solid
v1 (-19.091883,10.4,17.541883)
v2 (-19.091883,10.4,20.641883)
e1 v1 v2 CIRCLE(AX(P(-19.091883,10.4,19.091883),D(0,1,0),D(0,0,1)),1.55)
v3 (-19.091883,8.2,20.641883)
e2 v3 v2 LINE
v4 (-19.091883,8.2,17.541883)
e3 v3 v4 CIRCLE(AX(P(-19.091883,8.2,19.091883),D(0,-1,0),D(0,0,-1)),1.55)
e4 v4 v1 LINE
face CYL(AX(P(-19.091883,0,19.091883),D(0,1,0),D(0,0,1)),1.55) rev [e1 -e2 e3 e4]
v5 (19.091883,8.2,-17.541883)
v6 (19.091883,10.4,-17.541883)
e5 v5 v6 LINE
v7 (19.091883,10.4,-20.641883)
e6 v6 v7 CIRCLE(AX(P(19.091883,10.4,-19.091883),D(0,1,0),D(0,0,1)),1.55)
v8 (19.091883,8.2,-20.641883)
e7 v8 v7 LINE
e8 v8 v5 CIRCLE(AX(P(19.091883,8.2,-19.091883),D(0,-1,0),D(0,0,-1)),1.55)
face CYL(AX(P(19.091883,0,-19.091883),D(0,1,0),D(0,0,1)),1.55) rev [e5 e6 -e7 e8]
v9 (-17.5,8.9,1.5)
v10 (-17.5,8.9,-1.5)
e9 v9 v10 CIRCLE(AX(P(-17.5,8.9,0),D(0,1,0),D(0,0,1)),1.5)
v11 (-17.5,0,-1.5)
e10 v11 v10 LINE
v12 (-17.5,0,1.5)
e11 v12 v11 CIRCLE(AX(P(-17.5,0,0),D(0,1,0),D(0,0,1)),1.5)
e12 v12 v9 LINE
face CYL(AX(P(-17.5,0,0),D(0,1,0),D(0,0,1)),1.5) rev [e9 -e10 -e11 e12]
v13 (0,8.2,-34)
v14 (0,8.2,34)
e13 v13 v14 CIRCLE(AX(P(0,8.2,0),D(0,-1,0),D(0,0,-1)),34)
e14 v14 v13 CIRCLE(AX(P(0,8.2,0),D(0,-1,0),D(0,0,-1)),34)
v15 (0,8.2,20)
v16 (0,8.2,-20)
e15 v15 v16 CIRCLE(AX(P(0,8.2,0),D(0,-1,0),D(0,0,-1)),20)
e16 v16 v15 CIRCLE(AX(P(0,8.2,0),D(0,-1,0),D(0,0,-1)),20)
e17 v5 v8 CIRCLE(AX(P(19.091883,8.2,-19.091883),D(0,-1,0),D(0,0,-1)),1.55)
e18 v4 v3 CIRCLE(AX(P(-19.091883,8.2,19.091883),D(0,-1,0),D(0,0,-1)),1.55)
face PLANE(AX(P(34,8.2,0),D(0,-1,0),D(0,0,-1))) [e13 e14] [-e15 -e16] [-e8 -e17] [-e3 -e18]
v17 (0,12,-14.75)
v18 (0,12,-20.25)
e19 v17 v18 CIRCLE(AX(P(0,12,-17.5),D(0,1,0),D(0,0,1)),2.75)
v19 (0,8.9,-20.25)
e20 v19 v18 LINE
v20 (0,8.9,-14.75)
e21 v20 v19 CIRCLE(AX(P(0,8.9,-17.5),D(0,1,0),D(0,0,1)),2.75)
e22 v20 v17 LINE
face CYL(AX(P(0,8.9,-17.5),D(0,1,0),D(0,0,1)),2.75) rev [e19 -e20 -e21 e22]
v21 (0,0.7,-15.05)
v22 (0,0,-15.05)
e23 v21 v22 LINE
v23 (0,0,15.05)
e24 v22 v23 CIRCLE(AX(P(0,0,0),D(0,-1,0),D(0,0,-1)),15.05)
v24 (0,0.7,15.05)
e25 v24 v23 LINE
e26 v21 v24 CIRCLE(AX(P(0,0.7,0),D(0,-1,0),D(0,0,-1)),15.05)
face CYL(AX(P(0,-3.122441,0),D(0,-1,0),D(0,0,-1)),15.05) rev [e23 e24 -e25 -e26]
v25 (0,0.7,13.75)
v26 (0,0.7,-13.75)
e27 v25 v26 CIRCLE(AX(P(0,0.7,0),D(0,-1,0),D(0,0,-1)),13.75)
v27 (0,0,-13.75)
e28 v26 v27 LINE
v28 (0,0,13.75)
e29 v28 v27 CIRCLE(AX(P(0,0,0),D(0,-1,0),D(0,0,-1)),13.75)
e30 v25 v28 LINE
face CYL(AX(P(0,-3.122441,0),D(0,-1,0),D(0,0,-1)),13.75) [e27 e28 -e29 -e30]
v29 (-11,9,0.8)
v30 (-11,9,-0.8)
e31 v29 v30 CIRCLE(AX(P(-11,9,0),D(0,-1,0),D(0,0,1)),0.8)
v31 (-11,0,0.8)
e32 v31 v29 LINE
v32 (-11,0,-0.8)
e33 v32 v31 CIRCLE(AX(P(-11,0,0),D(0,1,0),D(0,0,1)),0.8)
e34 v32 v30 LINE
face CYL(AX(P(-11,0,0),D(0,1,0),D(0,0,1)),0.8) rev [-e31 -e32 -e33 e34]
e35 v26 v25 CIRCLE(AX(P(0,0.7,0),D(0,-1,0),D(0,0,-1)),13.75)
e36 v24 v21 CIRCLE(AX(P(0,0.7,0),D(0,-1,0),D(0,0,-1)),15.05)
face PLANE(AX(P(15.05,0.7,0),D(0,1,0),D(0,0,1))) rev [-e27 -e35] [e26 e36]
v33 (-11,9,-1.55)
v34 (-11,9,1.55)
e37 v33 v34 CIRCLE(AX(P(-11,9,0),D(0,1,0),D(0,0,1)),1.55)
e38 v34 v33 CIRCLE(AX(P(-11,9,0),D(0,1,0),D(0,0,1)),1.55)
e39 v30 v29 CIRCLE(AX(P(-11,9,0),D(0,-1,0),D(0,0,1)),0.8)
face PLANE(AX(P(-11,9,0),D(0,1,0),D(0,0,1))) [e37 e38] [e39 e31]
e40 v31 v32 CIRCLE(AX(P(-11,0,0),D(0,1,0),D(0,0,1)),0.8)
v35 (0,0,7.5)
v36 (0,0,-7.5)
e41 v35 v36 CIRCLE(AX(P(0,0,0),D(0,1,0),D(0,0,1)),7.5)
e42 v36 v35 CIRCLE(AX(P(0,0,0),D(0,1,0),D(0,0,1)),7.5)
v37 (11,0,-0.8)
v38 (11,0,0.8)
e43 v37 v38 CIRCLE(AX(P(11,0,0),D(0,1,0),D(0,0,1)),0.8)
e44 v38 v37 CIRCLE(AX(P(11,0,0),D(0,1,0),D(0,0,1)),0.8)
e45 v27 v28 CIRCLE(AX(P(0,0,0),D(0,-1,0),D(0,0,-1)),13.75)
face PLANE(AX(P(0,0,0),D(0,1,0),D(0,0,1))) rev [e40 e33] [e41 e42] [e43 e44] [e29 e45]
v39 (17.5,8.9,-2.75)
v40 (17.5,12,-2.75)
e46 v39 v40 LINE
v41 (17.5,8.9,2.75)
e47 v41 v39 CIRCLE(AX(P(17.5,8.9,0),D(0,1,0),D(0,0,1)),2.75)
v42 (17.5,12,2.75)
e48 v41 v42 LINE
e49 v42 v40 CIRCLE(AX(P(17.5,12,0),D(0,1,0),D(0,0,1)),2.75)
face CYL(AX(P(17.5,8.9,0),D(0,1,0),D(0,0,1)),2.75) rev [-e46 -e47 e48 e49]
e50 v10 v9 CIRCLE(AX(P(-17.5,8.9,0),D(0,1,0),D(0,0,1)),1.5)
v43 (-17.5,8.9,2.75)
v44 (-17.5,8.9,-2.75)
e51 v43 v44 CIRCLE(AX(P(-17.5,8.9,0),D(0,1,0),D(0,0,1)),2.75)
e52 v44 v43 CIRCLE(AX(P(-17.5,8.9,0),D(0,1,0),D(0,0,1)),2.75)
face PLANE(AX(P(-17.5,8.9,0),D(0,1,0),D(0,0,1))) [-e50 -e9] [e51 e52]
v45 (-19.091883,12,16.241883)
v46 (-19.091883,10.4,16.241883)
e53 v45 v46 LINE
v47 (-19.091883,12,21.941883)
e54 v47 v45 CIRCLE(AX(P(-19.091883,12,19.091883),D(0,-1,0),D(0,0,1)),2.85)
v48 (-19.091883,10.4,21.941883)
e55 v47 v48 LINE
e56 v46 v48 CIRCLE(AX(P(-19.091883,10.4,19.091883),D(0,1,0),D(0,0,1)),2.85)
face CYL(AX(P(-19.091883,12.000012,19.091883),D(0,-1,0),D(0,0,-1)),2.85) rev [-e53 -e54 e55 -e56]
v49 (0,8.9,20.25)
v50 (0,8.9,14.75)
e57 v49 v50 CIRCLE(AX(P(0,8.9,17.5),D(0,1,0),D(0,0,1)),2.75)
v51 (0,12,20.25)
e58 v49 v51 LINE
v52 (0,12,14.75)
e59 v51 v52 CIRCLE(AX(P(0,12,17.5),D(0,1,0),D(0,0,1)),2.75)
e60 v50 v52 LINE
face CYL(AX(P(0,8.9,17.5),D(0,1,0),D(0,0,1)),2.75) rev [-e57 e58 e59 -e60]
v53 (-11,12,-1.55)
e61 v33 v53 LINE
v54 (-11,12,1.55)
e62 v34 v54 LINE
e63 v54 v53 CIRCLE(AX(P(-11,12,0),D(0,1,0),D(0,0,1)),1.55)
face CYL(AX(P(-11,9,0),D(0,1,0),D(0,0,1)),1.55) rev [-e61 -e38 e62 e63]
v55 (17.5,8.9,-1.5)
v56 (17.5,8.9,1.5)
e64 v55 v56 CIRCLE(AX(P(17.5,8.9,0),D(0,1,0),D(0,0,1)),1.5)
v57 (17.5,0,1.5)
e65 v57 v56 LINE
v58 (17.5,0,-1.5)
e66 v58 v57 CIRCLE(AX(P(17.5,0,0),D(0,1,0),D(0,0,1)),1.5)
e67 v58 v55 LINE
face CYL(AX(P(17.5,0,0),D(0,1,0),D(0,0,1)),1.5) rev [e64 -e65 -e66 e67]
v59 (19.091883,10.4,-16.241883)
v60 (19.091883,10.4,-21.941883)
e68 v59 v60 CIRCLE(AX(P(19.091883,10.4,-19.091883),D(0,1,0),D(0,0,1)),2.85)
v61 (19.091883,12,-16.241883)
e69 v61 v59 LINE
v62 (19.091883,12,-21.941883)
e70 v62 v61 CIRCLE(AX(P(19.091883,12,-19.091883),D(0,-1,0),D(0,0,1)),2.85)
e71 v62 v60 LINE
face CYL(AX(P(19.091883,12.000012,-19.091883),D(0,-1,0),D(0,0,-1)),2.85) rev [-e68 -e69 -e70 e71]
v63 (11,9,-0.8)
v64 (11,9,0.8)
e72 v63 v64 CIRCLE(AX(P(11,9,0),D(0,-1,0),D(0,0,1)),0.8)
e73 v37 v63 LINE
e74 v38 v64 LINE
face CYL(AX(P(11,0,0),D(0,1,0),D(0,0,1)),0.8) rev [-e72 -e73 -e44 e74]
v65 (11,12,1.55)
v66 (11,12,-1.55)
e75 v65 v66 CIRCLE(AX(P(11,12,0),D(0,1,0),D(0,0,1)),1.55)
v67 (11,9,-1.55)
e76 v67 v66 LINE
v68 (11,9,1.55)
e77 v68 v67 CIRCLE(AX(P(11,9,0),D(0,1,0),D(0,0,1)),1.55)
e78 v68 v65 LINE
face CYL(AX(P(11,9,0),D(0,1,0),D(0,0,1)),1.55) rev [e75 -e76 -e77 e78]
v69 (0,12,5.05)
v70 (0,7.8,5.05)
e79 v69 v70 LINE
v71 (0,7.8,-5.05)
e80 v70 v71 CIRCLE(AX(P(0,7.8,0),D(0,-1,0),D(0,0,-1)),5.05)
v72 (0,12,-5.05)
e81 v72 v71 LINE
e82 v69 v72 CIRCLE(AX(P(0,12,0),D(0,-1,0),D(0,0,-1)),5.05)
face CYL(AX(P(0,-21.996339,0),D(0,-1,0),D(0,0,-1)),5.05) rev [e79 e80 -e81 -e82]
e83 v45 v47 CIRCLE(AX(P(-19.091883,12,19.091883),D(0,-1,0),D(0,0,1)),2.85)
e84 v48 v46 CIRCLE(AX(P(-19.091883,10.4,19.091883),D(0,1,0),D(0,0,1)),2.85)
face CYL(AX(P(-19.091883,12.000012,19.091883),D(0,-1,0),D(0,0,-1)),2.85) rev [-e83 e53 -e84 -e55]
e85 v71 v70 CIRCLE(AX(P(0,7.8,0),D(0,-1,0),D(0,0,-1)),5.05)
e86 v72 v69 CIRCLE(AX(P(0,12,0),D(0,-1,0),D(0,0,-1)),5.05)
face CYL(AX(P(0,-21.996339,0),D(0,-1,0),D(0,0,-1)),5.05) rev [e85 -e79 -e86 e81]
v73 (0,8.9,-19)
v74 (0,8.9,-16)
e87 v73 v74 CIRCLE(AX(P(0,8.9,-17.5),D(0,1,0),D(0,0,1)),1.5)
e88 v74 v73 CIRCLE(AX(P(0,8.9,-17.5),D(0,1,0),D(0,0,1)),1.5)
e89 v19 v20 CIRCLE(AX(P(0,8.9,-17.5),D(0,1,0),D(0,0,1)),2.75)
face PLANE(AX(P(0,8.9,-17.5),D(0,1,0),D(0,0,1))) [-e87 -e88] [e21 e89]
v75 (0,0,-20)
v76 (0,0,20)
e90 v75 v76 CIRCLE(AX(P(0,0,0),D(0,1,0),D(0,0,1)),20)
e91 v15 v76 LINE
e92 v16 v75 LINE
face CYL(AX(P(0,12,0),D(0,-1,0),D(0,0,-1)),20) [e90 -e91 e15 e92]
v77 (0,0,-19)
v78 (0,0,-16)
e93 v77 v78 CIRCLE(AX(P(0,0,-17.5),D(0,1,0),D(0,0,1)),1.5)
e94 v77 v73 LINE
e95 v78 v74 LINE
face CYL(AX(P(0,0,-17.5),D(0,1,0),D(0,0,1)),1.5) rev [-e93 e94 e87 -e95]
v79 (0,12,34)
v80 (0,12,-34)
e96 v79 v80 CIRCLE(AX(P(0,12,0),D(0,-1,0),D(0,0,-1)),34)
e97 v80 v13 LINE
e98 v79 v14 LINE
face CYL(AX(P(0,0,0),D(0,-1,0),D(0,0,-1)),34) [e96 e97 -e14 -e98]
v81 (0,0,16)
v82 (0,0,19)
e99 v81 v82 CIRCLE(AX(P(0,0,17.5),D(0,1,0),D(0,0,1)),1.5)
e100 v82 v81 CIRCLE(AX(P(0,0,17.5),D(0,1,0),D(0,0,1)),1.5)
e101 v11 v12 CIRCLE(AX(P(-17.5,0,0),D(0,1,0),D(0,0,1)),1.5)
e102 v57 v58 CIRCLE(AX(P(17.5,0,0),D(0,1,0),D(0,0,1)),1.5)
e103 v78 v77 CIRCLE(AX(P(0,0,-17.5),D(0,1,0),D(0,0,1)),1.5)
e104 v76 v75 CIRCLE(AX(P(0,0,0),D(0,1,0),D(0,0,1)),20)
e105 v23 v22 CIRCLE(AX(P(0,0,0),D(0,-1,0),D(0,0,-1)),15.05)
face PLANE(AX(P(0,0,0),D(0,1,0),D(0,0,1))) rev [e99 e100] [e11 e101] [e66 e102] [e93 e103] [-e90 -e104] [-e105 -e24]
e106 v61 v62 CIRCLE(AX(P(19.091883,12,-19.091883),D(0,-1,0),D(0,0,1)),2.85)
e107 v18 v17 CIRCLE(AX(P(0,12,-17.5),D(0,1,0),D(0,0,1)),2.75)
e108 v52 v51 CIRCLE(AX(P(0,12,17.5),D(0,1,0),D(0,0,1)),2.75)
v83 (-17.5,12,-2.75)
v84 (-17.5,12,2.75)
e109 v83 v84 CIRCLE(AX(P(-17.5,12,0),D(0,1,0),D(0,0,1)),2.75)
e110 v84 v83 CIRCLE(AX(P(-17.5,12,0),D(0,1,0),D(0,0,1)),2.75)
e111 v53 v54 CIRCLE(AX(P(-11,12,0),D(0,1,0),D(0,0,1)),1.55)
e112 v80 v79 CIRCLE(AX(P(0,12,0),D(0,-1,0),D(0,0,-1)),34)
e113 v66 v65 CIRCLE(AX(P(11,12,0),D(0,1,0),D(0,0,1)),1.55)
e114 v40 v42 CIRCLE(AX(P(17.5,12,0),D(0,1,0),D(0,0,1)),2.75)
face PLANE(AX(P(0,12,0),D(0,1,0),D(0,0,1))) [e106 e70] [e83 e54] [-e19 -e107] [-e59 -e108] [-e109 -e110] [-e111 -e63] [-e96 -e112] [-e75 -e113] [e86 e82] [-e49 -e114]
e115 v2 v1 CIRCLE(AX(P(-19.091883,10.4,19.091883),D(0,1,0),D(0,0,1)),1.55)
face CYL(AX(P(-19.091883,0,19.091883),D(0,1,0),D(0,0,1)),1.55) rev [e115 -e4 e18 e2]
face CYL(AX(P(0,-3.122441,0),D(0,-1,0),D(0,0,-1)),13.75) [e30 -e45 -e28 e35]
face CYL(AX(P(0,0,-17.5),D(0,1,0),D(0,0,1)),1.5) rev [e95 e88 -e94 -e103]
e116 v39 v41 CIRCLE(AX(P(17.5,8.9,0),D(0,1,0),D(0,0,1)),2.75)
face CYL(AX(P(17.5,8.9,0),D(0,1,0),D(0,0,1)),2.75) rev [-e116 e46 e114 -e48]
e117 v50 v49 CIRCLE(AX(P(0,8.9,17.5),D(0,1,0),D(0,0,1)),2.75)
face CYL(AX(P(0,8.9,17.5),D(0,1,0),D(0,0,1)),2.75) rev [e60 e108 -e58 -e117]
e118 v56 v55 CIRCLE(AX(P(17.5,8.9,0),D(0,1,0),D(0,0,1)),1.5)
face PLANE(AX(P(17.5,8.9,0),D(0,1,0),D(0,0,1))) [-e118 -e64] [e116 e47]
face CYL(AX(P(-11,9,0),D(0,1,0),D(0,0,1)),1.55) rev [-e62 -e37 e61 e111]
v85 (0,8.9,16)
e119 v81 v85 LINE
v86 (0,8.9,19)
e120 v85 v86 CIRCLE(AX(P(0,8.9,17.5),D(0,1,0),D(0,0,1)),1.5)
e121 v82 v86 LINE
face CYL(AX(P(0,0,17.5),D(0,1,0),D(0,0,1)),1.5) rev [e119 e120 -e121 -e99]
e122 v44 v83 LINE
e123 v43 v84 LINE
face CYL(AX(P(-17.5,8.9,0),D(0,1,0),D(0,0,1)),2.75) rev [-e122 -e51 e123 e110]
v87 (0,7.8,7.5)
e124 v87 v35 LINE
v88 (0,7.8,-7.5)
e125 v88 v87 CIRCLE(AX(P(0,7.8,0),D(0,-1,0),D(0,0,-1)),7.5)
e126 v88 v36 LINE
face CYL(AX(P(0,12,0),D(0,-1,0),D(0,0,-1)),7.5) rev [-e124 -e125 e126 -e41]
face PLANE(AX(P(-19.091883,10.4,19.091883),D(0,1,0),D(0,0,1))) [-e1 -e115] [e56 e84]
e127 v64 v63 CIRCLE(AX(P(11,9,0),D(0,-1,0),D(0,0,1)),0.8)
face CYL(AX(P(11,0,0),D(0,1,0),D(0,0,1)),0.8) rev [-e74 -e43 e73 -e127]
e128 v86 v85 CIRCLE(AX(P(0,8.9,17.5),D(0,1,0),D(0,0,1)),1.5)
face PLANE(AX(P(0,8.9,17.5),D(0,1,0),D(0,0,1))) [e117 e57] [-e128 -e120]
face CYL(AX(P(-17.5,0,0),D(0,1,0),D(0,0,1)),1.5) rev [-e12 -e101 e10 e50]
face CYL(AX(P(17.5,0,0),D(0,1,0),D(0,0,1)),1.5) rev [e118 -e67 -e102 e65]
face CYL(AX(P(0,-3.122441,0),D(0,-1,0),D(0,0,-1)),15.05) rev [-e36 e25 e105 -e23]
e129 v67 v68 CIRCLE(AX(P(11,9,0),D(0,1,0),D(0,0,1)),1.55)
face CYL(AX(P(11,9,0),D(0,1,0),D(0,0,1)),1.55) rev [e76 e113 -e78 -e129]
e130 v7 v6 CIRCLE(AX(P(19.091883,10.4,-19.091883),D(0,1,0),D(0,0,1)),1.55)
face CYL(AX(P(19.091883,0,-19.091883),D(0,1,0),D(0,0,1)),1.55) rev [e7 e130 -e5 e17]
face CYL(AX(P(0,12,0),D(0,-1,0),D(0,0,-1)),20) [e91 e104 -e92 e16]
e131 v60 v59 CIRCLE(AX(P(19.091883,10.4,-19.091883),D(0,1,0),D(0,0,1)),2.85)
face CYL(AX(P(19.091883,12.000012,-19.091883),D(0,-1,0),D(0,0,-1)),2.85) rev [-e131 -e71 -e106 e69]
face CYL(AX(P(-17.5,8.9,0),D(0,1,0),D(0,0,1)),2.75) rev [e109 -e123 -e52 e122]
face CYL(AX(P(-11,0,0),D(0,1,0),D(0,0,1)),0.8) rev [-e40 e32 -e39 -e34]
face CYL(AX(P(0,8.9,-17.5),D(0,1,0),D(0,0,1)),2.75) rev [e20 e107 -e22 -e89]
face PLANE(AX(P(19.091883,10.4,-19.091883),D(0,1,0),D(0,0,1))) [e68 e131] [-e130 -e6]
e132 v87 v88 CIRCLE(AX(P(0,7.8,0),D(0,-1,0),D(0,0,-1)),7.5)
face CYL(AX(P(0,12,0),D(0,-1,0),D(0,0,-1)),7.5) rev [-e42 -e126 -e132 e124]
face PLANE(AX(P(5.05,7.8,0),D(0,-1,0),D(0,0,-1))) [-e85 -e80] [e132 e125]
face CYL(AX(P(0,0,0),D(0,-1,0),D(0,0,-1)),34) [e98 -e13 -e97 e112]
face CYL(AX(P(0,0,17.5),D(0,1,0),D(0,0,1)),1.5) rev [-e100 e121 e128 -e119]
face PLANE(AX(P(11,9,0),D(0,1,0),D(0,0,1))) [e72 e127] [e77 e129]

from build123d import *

# Parameters (mm, degrees)
SKETCH1_R               = 20
SKETCH1_R_2             = 7.5
BOSS_EXTRUDE1_DEPTH     = 12
SKETCH9_W               = 1.3
SKETCH9_H               = 0.7
SKETCH12_W              = 14
SKETCH12_H              = 3.8
SKETCH5_R               = 0.8
CUT_EXTRUDE2_DEPTH      = 50.558046773
SKETCH11_R              = 2.75
SKETCH11_R_2            = 1.5
CUT_EXTRUDE4_DEPTH      = 3.1
SKETCH14_W              = 4.95
SKETCH14_H              = 4.2
CUT_EXTRUDE5_DEPTH      = 50.558046773
CUT_EXTRUDE5_DEPTH_BACK = 1.6
SKETCH15_R              = 2.85
SKETCH7_R               = 1.55
CUT_EXTRUDE3_DEPTH      = 3
SKETCH16_R              = 1.55
CUT_EXTRUDE6_DEPTH      = 50.195121709
SKETCH17_R              = 1.55
CUT_EXTRUDE7_DEPTH      = 50.195121709
SKETCH18_R              = 1.5
CUT_EXTRUDE8_DEPTH      = 50.558046773


with BuildPart() as part:
    # Sketch1 → Boss-Extrude1 (new body)
    with BuildSketch(Plane(origin=(0, 0, 0), x_dir=(1, 0, 0), z_dir=(0, 1, 0))):
        with Locations(Location((0, 0, 0), (0, 0, 270))):
            Circle(SKETCH1_R)
        with Locations(Location((0, 0, 0), (0, 0, 270))):
            Circle(SKETCH1_R_2, mode=Mode.SUBTRACT)
    extrude(amount=BOSS_EXTRUDE1_DEPTH)

    # Sketch9 → Cut-Revolve3 (revolve, cut)
    with BuildSketch(Plane.XY, mode=Mode.PRIVATE) as cut_revolve3_sk:
        with Locations((14.4, 0.35)):
            Rectangle(SKETCH9_W, SKETCH9_H)
    revolve(cut_revolve3_sk.sketch.rotate(Axis((0, -3.122441051, 0), (0, 1, 0)), 90), axis=Axis((0, -3.122441051, 0), (0, 1, 0)), mode=Mode.SUBTRACT)

    # Sketch12 → Revolve1 (revolve)
    with BuildSketch(Plane.XY, mode=Mode.PRIVATE) as revolve1_sk:
        with Locations((27, 10.1)):
            Rectangle(SKETCH12_W, SKETCH12_H)
    revolve(revolve1_sk.sketch.rotate(Axis((0, 0, 0), (0, 1, 0)), 90), axis=Axis((0, 0, 0), (0, 1, 0)))

    # Sketch5 → Cut-Extrude2 (cut, through all)
    with BuildSketch(Plane(origin=(0, 12, 0), x_dir=(1, 0, 0), z_dir=(0, 1, 0))):
        with Locations(Location((11, 0, 0), (0, 0, 270))):
            Circle(SKETCH5_R)
        with Locations(Location((-11, 0, 0), (0, 0, 270))):
            Circle(SKETCH5_R)
    extrude(amount=-CUT_EXTRUDE2_DEPTH, mode=Mode.SUBTRACT)

    # Sketch11 → Cut-Extrude4 (cut)
    # profile 1 of 4: a face of its own
    with BuildSketch(Plane(origin=(0, 12, 0), x_dir=(1, 0, 0), z_dir=(0, 1, 0))):
        with Locations(Location((-17.5, 0, 0), (0, 0, 270))):
            Circle(SKETCH11_R)
        with Locations(Location((-17.5, 0, 0), (0, 0, 270))):
            Circle(SKETCH11_R_2, mode=Mode.SUBTRACT)
    # profile 2 of 4: a face of its own
    with BuildSketch(Plane(origin=(0, 12, 0), x_dir=(1, 0, 0), z_dir=(0, 1, 0))):
        with Locations(Location((0, 17.5, 0), (0, 0, 270))):
            Circle(SKETCH11_R)
        with Locations(Location((0, 17.5, 0), (0, 0, 270))):
            Circle(SKETCH11_R_2, mode=Mode.SUBTRACT)
    # profile 3 of 4: a face of its own
    with BuildSketch(Plane(origin=(0, 12, 0), x_dir=(1, 0, 0), z_dir=(0, 1, 0))):
        with Locations(Location((17.5, 0, 0), (0, 0, 270))):
            Circle(SKETCH11_R)
        with Locations(Location((17.5, 0, 0), (0, 0, 270))):
            Circle(SKETCH11_R_2, mode=Mode.SUBTRACT)
    # profile 4 of 4: a face of its own
    with BuildSketch(Plane(origin=(0, 12, 0), x_dir=(1, 0, 0), z_dir=(0, 1, 0))):
        with Locations(Location((0, -17.5, 0), (0, 0, 270))):
            Circle(SKETCH11_R)
        with Locations(Location((0, -17.5, 0), (0, 0, 270))):
            Circle(SKETCH11_R_2, mode=Mode.SUBTRACT)
    extrude(amount=-CUT_EXTRUDE4_DEPTH, mode=Mode.SUBTRACT)

    # Sketch14 → Revolve2 (revolve)
    with BuildSketch(Plane.XY, mode=Mode.PRIVATE) as revolve2_sk:
        with Locations((7.525, 9.9)):
            Rectangle(SKETCH14_W, SKETCH14_H)
    revolve(revolve2_sk.sketch.rotate(Axis((0, -21.99633859, 0), (0, 1, 0)), 90), axis=Axis((0, -21.99633859, 0), (0, 1, 0)))

    # Sketch15 → Cut-Extrude5 (cut, two sides: drawn at the far end of the back side and taken through both)
    with BuildSketch(Plane(origin=(0, 12, 0), x_dir=(1, 0, 0), z_dir=(0, 1, 0)).offset(-CUT_EXTRUDE5_DEPTH_BACK)):
        with Locations(Location((-19.091883092, -19.091883092, 0), (0, 0, 90))):
            Circle(SKETCH15_R)
        with Locations(Location((19.091883092, 19.091883092, 0), (0, 0, 90))):
            Circle(SKETCH15_R)
    extrude(amount=CUT_EXTRUDE5_DEPTH + CUT_EXTRUDE5_DEPTH_BACK, mode=Mode.SUBTRACT)

    # Sketch7 → Cut-Extrude3 (cut)
    with BuildSketch(Plane(origin=(0, 12, 0), x_dir=(1, 0, 0), z_dir=(0, 1, 0))):
        with Locations(Location((11, 0, 0), (0, 0, 270))):
            Circle(SKETCH7_R)
        with Locations(Location((-11, 0, 0), (0, 0, 270))):
            Circle(SKETCH7_R)
    extrude(amount=-CUT_EXTRUDE3_DEPTH, mode=Mode.SUBTRACT)

    # Sketch16 → Cut-Extrude6 (cut, through all)
    with BuildSketch(Plane(origin=(0, 10.4, 0), x_dir=(1, 0, 0), z_dir=(0, 1, 0))):
        with Locations(Location((-19.091883092, -19.091883092, 0), (0, 0, 270))):
            Circle(SKETCH16_R)
    extrude(amount=-CUT_EXTRUDE6_DEPTH, mode=Mode.SUBTRACT)

    # Sketch17 → Cut-Extrude7 (cut, through all)
    with BuildSketch(Plane(origin=(0, 10.4, 0), x_dir=(1, 0, 0), z_dir=(0, 1, 0))):
        with Locations(Location((19.091883092, 19.091883092, 0), (0, 0, 270))):
            Circle(SKETCH17_R)
    extrude(amount=-CUT_EXTRUDE7_DEPTH, mode=Mode.SUBTRACT)

    # Sketch18 → Cut-Extrude8 (cut, through all)
    with BuildSketch(Plane(origin=(0, 12, 0), x_dir=(1, 0, 0), z_dir=(0, 1, 0))):
        with Locations(Location((0, 17.5, 0), (0, 0, 270))):
            Circle(SKETCH18_R)
        with Locations(Location((-17.5, 0, 0), (0, 0, 270))):
            Circle(SKETCH18_R)
        with Locations(Location((0, -17.5, 0), (0, 0, 270))):
            Circle(SKETCH18_R)
        with Locations(Location((17.5, 0, 0), (0, 0, 270))):
            Circle(SKETCH18_R)
    extrude(amount=-CUT_EXTRUDE8_DEPTH, mode=Mode.SUBTRACT)


solid = part.part
